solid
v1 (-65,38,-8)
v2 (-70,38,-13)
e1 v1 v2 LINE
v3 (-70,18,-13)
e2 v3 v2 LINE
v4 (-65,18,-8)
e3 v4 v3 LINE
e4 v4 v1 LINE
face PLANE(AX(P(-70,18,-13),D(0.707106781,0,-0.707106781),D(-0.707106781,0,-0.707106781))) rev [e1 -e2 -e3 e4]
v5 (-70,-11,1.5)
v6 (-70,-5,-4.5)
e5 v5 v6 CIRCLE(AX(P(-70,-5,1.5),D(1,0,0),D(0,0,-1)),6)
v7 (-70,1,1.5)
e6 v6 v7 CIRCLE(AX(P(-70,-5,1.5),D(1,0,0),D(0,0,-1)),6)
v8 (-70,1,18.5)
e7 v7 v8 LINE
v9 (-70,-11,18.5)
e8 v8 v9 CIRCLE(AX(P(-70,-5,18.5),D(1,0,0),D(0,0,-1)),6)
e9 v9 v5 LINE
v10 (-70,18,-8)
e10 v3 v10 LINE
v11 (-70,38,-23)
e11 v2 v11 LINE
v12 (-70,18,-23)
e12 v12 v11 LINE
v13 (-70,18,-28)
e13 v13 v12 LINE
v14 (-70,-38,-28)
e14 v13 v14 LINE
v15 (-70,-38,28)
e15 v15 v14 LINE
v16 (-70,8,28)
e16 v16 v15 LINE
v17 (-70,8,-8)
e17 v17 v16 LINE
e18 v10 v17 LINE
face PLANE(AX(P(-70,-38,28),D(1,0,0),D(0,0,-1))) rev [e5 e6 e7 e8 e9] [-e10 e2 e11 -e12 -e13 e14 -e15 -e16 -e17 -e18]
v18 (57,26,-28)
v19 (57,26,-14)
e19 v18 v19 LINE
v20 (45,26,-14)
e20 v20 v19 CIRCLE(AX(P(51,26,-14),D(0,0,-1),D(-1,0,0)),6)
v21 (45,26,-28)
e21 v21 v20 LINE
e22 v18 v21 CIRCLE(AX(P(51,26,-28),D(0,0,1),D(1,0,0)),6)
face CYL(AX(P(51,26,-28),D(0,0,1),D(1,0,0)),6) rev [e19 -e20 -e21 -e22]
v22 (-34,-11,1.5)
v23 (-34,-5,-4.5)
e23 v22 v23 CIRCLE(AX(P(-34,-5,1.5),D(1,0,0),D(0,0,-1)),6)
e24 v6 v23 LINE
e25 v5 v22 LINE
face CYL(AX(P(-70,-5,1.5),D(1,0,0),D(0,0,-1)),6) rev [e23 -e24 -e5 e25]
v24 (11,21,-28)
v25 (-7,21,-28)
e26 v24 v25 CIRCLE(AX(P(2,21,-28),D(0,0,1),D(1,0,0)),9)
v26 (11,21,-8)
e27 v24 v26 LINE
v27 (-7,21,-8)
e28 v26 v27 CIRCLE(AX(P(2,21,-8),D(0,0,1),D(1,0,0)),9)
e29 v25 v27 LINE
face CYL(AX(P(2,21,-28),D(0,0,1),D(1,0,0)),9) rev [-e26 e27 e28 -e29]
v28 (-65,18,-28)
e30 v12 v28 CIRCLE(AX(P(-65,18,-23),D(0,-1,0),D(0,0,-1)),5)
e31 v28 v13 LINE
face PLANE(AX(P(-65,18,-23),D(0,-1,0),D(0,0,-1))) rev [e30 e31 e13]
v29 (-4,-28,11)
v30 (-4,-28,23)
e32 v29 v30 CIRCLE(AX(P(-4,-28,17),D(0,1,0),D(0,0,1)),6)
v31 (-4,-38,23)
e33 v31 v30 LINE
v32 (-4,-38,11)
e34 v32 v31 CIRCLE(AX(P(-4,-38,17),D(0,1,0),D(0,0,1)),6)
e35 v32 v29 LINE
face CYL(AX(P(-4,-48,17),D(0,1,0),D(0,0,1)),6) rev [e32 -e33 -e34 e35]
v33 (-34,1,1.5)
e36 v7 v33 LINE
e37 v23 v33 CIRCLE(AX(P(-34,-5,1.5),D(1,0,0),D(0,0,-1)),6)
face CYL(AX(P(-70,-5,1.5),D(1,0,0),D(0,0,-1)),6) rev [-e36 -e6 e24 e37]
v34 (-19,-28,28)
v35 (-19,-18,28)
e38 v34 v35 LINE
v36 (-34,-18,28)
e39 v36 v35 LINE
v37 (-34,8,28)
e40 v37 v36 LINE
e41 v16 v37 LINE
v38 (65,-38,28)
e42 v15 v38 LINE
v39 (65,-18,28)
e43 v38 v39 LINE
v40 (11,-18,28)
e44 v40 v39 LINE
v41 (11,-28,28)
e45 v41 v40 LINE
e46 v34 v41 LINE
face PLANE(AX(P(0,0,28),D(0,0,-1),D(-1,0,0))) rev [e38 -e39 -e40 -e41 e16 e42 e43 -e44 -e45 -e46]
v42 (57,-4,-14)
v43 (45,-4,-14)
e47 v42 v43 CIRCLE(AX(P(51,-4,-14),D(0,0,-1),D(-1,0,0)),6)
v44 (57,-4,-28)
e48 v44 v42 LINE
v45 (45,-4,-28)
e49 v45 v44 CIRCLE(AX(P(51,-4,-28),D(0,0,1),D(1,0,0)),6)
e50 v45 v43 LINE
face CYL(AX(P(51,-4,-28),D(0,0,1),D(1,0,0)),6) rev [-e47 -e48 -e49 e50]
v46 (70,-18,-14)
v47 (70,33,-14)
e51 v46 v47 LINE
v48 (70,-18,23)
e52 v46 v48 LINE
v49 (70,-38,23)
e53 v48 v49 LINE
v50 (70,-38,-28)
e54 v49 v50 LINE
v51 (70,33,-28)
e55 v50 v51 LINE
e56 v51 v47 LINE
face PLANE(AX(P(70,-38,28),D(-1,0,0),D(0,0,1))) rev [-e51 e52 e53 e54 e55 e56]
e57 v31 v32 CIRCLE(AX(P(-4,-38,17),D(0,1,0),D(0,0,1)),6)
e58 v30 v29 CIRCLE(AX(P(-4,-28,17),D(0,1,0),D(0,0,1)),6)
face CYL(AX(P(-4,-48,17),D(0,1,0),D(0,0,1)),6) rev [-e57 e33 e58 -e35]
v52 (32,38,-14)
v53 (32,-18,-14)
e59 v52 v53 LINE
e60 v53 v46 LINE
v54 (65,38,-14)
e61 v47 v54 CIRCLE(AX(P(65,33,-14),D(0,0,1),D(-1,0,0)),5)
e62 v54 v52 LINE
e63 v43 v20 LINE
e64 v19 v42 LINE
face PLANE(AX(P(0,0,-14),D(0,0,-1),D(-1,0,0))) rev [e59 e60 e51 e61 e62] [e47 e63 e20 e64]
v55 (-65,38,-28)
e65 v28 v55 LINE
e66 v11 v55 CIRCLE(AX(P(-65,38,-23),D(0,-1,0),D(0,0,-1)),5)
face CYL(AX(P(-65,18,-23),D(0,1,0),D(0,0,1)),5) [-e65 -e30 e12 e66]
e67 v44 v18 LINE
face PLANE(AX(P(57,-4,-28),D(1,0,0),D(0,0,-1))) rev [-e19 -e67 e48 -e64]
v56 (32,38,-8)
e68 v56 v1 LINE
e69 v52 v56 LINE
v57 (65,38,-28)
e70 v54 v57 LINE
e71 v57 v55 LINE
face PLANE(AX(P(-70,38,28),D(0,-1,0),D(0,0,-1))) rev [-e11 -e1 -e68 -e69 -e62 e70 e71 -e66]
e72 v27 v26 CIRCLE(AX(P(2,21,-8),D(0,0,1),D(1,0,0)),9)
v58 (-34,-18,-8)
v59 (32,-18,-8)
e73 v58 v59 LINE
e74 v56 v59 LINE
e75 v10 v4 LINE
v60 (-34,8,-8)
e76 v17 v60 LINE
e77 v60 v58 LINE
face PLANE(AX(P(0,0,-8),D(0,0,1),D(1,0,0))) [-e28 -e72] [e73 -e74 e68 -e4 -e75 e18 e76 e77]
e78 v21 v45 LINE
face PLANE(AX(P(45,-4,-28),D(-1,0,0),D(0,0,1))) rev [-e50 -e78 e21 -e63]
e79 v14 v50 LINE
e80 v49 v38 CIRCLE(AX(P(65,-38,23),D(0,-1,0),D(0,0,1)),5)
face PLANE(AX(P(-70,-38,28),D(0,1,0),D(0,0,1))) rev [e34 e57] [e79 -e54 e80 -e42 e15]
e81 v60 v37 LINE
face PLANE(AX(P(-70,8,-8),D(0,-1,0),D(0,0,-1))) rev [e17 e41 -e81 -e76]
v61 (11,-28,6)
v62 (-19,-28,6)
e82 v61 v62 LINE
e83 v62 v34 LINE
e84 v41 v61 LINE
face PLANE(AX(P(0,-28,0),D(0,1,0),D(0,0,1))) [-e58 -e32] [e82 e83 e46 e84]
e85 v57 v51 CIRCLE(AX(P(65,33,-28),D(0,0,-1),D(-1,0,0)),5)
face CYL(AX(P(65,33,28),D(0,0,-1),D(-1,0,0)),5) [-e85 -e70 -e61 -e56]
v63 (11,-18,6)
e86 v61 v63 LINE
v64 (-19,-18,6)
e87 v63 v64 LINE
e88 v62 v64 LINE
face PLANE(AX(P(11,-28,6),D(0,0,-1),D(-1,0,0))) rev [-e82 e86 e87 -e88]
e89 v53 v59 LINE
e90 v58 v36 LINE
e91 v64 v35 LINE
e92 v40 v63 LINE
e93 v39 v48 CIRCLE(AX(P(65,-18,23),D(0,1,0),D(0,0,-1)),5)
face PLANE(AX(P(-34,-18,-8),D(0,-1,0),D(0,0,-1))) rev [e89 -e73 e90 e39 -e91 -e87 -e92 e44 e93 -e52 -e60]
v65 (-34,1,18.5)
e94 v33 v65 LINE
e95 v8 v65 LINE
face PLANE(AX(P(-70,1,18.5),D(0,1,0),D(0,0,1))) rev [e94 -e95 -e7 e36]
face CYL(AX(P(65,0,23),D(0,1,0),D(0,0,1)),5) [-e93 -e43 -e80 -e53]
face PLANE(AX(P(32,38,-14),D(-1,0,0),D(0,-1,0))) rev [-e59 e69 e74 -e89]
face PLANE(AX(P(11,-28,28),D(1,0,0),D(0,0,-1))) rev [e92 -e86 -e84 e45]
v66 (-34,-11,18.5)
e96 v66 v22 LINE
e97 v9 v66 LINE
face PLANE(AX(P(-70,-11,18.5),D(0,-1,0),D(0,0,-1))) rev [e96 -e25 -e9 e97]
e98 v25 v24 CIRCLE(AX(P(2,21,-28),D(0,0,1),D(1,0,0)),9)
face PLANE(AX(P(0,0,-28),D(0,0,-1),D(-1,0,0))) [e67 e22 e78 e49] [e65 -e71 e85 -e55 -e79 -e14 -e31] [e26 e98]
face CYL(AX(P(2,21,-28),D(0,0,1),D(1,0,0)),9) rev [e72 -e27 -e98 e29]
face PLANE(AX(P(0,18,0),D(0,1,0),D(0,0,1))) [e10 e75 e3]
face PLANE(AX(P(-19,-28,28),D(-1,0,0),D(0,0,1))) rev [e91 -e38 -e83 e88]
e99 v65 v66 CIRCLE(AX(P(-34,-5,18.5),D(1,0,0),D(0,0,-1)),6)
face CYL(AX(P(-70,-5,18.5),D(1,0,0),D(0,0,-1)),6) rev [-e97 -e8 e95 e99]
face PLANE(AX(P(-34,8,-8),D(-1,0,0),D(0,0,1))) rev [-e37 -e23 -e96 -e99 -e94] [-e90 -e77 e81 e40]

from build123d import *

# Parameters (mm, degrees)
L_BRACKET_PROFILE_SKETCH_W     = 140
L_BRACKET_PROFILE_SKETCH_H     = 76
L_BRACKET_BASE_DEPTH           = 28
STEPPED_BLOCK_CUT_DEPTH        = 36
RECTANGULAR_POCKET_SKETCH_W    = 30
RECTANGULAR_POCKET_SKETCH_H    = 22
RECTANGULAR_POCKET_30X22_DEPTH = 10
UPRIGHT_RECESS_SKETCH_W        = 38
UPRIGHT_RECESS_SKETCH_H        = 56
UPRIGHT_FACE_RECESS_DEPTH      = 6
UPRIGHT_SLOT_AND_HOLE_SKETCH_R = 9
UPRIGHT_SLOT_AND_HOLE_DEPTH    = 88.407093534
CORNER_NOTCH_DEPTH             = 20
HORIZONTAL_SLOT_9_5_WIDE_DEPTH = 115.210332282
POCKET_HOLE_SKETCH_R           = 6
POCKET_HOLE_12_DEPTH           = 20
EDGE_FILLETS_R5_R              = 5


with BuildPart() as part:
    # L-Bracket Profile Sketch → L-Bracket Base (new, symmetric)
    with BuildSketch(Plane.XY):
        Rectangle(L_BRACKET_PROFILE_SKETCH_W, L_BRACKET_PROFILE_SKETCH_H)
    extrude(amount=L_BRACKET_BASE_DEPTH, both=True)

    # Step Cut Sketch → Stepped Block Cut (cut)
    with BuildSketch(Plane.XY.offset(28)):
        Polygon((-70, 8), (-34, 8), (-34, -18), (70, -18), (70, 38), (-70, 38), align=None)
    extrude(amount=-STEPPED_BLOCK_CUT_DEPTH, mode=Mode.SUBTRACT)

    # Rectangular Pocket Sketch → Rectangular Pocket 30x22 (cut)
    with BuildSketch(Plane(origin=(0, -18, 0), x_dir=(1, 0, 0), z_dir=(0, 1, 0))):
        with Locations((-4, -17)):
            Rectangle(RECTANGULAR_POCKET_SKETCH_W, RECTANGULAR_POCKET_SKETCH_H)
    extrude(amount=-RECTANGULAR_POCKET_30X22_DEPTH, mode=Mode.SUBTRACT)

    # Upright Recess Sketch → Upright Face Recess (cut)
    with BuildSketch(Plane.XY.offset(-8)):
        with Locations((51, 10)):
            Rectangle(UPRIGHT_RECESS_SKETCH_W, UPRIGHT_RECESS_SKETCH_H)
    extrude(amount=-UPRIGHT_FACE_RECESS_DEPTH, mode=Mode.SUBTRACT)

    # Upright Slot and Hole Sketch → Upright Slot and Hole (cut, through all)
    with BuildSketch(Plane.XY.offset(-8)):
        with Locations((2, 21)):
            Circle(UPRIGHT_SLOT_AND_HOLE_SKETCH_R)
        with BuildLine():
            Line((45, -4), (45, 26))
            ThreePointArc((45, 26), (51, 32), (57, 26))
            Line((57, 26), (57, -4))
            ThreePointArc((57, -4), (51, -10), (45, -4))
        make_face()
    extrude(amount=-UPRIGHT_SLOT_AND_HOLE_DEPTH, mode=Mode.SUBTRACT)

    # Corner Notch Sketch → Corner Notch (cut)
    with BuildSketch(Plane(origin=(0, 38, 0), x_dir=(1, 0, 0), z_dir=(0, 1, 0))):
        Polygon((-70, 13), (-65, 8), (-70, 8), align=None)
        with BuildLine():
            Line((-70, 23), (-70, 28))
            Line((-70, 28), (-65, 28))
            ThreePointArc((-65, 28), (-68.535533906, 26.535533906), (-70, 23))
        make_face()
    extrude(amount=-CORNER_NOTCH_DEPTH, mode=Mode.SUBTRACT)

    # Horizontal Slot Sketch → Horizontal Slot 9.5 Wide (cut, through all)
    with BuildSketch(Plane(origin=(-34, 0, 0), x_dir=(0, 0, -1), z_dir=(1, 0, 0))):
        with BuildLine():
            Line((-18.5, 1), (-1.5, 1))
            ThreePointArc((-1.5, 1), (4.5, -5), (-1.5, -11))
            Line((-1.5, -11), (-18.5, -11))
            ThreePointArc((-18.5, -11), (-24.5, -5), (-18.5, 1))
        make_face()
    extrude(amount=-HORIZONTAL_SLOT_9_5_WIDE_DEPTH, mode=Mode.SUBTRACT)

    # Pocket Hole Sketch → Pocket Hole Ø12 (cut)
    with BuildSketch(Plane(origin=(0, -28, 0), x_dir=(1, 0, 0), z_dir=(0, 1, 0))):
        with Locations(Location((-4, -17, 0), (0, 0, 270))):
            Circle(POCKET_HOLE_SKETCH_R)
    extrude(amount=-POCKET_HOLE_12_DEPTH, mode=Mode.SUBTRACT)

    # Edge Fillets R5
    edge_fillets_r5_edges = [part.edges().sort_by_distance(p)[0] for p in [
        (70, -28, 28),
        (70, 38, -21),
    ]]
    fillet(edge_fillets_r5_edges, radius=EDGE_FILLETS_R5_R)


solid = part.part
